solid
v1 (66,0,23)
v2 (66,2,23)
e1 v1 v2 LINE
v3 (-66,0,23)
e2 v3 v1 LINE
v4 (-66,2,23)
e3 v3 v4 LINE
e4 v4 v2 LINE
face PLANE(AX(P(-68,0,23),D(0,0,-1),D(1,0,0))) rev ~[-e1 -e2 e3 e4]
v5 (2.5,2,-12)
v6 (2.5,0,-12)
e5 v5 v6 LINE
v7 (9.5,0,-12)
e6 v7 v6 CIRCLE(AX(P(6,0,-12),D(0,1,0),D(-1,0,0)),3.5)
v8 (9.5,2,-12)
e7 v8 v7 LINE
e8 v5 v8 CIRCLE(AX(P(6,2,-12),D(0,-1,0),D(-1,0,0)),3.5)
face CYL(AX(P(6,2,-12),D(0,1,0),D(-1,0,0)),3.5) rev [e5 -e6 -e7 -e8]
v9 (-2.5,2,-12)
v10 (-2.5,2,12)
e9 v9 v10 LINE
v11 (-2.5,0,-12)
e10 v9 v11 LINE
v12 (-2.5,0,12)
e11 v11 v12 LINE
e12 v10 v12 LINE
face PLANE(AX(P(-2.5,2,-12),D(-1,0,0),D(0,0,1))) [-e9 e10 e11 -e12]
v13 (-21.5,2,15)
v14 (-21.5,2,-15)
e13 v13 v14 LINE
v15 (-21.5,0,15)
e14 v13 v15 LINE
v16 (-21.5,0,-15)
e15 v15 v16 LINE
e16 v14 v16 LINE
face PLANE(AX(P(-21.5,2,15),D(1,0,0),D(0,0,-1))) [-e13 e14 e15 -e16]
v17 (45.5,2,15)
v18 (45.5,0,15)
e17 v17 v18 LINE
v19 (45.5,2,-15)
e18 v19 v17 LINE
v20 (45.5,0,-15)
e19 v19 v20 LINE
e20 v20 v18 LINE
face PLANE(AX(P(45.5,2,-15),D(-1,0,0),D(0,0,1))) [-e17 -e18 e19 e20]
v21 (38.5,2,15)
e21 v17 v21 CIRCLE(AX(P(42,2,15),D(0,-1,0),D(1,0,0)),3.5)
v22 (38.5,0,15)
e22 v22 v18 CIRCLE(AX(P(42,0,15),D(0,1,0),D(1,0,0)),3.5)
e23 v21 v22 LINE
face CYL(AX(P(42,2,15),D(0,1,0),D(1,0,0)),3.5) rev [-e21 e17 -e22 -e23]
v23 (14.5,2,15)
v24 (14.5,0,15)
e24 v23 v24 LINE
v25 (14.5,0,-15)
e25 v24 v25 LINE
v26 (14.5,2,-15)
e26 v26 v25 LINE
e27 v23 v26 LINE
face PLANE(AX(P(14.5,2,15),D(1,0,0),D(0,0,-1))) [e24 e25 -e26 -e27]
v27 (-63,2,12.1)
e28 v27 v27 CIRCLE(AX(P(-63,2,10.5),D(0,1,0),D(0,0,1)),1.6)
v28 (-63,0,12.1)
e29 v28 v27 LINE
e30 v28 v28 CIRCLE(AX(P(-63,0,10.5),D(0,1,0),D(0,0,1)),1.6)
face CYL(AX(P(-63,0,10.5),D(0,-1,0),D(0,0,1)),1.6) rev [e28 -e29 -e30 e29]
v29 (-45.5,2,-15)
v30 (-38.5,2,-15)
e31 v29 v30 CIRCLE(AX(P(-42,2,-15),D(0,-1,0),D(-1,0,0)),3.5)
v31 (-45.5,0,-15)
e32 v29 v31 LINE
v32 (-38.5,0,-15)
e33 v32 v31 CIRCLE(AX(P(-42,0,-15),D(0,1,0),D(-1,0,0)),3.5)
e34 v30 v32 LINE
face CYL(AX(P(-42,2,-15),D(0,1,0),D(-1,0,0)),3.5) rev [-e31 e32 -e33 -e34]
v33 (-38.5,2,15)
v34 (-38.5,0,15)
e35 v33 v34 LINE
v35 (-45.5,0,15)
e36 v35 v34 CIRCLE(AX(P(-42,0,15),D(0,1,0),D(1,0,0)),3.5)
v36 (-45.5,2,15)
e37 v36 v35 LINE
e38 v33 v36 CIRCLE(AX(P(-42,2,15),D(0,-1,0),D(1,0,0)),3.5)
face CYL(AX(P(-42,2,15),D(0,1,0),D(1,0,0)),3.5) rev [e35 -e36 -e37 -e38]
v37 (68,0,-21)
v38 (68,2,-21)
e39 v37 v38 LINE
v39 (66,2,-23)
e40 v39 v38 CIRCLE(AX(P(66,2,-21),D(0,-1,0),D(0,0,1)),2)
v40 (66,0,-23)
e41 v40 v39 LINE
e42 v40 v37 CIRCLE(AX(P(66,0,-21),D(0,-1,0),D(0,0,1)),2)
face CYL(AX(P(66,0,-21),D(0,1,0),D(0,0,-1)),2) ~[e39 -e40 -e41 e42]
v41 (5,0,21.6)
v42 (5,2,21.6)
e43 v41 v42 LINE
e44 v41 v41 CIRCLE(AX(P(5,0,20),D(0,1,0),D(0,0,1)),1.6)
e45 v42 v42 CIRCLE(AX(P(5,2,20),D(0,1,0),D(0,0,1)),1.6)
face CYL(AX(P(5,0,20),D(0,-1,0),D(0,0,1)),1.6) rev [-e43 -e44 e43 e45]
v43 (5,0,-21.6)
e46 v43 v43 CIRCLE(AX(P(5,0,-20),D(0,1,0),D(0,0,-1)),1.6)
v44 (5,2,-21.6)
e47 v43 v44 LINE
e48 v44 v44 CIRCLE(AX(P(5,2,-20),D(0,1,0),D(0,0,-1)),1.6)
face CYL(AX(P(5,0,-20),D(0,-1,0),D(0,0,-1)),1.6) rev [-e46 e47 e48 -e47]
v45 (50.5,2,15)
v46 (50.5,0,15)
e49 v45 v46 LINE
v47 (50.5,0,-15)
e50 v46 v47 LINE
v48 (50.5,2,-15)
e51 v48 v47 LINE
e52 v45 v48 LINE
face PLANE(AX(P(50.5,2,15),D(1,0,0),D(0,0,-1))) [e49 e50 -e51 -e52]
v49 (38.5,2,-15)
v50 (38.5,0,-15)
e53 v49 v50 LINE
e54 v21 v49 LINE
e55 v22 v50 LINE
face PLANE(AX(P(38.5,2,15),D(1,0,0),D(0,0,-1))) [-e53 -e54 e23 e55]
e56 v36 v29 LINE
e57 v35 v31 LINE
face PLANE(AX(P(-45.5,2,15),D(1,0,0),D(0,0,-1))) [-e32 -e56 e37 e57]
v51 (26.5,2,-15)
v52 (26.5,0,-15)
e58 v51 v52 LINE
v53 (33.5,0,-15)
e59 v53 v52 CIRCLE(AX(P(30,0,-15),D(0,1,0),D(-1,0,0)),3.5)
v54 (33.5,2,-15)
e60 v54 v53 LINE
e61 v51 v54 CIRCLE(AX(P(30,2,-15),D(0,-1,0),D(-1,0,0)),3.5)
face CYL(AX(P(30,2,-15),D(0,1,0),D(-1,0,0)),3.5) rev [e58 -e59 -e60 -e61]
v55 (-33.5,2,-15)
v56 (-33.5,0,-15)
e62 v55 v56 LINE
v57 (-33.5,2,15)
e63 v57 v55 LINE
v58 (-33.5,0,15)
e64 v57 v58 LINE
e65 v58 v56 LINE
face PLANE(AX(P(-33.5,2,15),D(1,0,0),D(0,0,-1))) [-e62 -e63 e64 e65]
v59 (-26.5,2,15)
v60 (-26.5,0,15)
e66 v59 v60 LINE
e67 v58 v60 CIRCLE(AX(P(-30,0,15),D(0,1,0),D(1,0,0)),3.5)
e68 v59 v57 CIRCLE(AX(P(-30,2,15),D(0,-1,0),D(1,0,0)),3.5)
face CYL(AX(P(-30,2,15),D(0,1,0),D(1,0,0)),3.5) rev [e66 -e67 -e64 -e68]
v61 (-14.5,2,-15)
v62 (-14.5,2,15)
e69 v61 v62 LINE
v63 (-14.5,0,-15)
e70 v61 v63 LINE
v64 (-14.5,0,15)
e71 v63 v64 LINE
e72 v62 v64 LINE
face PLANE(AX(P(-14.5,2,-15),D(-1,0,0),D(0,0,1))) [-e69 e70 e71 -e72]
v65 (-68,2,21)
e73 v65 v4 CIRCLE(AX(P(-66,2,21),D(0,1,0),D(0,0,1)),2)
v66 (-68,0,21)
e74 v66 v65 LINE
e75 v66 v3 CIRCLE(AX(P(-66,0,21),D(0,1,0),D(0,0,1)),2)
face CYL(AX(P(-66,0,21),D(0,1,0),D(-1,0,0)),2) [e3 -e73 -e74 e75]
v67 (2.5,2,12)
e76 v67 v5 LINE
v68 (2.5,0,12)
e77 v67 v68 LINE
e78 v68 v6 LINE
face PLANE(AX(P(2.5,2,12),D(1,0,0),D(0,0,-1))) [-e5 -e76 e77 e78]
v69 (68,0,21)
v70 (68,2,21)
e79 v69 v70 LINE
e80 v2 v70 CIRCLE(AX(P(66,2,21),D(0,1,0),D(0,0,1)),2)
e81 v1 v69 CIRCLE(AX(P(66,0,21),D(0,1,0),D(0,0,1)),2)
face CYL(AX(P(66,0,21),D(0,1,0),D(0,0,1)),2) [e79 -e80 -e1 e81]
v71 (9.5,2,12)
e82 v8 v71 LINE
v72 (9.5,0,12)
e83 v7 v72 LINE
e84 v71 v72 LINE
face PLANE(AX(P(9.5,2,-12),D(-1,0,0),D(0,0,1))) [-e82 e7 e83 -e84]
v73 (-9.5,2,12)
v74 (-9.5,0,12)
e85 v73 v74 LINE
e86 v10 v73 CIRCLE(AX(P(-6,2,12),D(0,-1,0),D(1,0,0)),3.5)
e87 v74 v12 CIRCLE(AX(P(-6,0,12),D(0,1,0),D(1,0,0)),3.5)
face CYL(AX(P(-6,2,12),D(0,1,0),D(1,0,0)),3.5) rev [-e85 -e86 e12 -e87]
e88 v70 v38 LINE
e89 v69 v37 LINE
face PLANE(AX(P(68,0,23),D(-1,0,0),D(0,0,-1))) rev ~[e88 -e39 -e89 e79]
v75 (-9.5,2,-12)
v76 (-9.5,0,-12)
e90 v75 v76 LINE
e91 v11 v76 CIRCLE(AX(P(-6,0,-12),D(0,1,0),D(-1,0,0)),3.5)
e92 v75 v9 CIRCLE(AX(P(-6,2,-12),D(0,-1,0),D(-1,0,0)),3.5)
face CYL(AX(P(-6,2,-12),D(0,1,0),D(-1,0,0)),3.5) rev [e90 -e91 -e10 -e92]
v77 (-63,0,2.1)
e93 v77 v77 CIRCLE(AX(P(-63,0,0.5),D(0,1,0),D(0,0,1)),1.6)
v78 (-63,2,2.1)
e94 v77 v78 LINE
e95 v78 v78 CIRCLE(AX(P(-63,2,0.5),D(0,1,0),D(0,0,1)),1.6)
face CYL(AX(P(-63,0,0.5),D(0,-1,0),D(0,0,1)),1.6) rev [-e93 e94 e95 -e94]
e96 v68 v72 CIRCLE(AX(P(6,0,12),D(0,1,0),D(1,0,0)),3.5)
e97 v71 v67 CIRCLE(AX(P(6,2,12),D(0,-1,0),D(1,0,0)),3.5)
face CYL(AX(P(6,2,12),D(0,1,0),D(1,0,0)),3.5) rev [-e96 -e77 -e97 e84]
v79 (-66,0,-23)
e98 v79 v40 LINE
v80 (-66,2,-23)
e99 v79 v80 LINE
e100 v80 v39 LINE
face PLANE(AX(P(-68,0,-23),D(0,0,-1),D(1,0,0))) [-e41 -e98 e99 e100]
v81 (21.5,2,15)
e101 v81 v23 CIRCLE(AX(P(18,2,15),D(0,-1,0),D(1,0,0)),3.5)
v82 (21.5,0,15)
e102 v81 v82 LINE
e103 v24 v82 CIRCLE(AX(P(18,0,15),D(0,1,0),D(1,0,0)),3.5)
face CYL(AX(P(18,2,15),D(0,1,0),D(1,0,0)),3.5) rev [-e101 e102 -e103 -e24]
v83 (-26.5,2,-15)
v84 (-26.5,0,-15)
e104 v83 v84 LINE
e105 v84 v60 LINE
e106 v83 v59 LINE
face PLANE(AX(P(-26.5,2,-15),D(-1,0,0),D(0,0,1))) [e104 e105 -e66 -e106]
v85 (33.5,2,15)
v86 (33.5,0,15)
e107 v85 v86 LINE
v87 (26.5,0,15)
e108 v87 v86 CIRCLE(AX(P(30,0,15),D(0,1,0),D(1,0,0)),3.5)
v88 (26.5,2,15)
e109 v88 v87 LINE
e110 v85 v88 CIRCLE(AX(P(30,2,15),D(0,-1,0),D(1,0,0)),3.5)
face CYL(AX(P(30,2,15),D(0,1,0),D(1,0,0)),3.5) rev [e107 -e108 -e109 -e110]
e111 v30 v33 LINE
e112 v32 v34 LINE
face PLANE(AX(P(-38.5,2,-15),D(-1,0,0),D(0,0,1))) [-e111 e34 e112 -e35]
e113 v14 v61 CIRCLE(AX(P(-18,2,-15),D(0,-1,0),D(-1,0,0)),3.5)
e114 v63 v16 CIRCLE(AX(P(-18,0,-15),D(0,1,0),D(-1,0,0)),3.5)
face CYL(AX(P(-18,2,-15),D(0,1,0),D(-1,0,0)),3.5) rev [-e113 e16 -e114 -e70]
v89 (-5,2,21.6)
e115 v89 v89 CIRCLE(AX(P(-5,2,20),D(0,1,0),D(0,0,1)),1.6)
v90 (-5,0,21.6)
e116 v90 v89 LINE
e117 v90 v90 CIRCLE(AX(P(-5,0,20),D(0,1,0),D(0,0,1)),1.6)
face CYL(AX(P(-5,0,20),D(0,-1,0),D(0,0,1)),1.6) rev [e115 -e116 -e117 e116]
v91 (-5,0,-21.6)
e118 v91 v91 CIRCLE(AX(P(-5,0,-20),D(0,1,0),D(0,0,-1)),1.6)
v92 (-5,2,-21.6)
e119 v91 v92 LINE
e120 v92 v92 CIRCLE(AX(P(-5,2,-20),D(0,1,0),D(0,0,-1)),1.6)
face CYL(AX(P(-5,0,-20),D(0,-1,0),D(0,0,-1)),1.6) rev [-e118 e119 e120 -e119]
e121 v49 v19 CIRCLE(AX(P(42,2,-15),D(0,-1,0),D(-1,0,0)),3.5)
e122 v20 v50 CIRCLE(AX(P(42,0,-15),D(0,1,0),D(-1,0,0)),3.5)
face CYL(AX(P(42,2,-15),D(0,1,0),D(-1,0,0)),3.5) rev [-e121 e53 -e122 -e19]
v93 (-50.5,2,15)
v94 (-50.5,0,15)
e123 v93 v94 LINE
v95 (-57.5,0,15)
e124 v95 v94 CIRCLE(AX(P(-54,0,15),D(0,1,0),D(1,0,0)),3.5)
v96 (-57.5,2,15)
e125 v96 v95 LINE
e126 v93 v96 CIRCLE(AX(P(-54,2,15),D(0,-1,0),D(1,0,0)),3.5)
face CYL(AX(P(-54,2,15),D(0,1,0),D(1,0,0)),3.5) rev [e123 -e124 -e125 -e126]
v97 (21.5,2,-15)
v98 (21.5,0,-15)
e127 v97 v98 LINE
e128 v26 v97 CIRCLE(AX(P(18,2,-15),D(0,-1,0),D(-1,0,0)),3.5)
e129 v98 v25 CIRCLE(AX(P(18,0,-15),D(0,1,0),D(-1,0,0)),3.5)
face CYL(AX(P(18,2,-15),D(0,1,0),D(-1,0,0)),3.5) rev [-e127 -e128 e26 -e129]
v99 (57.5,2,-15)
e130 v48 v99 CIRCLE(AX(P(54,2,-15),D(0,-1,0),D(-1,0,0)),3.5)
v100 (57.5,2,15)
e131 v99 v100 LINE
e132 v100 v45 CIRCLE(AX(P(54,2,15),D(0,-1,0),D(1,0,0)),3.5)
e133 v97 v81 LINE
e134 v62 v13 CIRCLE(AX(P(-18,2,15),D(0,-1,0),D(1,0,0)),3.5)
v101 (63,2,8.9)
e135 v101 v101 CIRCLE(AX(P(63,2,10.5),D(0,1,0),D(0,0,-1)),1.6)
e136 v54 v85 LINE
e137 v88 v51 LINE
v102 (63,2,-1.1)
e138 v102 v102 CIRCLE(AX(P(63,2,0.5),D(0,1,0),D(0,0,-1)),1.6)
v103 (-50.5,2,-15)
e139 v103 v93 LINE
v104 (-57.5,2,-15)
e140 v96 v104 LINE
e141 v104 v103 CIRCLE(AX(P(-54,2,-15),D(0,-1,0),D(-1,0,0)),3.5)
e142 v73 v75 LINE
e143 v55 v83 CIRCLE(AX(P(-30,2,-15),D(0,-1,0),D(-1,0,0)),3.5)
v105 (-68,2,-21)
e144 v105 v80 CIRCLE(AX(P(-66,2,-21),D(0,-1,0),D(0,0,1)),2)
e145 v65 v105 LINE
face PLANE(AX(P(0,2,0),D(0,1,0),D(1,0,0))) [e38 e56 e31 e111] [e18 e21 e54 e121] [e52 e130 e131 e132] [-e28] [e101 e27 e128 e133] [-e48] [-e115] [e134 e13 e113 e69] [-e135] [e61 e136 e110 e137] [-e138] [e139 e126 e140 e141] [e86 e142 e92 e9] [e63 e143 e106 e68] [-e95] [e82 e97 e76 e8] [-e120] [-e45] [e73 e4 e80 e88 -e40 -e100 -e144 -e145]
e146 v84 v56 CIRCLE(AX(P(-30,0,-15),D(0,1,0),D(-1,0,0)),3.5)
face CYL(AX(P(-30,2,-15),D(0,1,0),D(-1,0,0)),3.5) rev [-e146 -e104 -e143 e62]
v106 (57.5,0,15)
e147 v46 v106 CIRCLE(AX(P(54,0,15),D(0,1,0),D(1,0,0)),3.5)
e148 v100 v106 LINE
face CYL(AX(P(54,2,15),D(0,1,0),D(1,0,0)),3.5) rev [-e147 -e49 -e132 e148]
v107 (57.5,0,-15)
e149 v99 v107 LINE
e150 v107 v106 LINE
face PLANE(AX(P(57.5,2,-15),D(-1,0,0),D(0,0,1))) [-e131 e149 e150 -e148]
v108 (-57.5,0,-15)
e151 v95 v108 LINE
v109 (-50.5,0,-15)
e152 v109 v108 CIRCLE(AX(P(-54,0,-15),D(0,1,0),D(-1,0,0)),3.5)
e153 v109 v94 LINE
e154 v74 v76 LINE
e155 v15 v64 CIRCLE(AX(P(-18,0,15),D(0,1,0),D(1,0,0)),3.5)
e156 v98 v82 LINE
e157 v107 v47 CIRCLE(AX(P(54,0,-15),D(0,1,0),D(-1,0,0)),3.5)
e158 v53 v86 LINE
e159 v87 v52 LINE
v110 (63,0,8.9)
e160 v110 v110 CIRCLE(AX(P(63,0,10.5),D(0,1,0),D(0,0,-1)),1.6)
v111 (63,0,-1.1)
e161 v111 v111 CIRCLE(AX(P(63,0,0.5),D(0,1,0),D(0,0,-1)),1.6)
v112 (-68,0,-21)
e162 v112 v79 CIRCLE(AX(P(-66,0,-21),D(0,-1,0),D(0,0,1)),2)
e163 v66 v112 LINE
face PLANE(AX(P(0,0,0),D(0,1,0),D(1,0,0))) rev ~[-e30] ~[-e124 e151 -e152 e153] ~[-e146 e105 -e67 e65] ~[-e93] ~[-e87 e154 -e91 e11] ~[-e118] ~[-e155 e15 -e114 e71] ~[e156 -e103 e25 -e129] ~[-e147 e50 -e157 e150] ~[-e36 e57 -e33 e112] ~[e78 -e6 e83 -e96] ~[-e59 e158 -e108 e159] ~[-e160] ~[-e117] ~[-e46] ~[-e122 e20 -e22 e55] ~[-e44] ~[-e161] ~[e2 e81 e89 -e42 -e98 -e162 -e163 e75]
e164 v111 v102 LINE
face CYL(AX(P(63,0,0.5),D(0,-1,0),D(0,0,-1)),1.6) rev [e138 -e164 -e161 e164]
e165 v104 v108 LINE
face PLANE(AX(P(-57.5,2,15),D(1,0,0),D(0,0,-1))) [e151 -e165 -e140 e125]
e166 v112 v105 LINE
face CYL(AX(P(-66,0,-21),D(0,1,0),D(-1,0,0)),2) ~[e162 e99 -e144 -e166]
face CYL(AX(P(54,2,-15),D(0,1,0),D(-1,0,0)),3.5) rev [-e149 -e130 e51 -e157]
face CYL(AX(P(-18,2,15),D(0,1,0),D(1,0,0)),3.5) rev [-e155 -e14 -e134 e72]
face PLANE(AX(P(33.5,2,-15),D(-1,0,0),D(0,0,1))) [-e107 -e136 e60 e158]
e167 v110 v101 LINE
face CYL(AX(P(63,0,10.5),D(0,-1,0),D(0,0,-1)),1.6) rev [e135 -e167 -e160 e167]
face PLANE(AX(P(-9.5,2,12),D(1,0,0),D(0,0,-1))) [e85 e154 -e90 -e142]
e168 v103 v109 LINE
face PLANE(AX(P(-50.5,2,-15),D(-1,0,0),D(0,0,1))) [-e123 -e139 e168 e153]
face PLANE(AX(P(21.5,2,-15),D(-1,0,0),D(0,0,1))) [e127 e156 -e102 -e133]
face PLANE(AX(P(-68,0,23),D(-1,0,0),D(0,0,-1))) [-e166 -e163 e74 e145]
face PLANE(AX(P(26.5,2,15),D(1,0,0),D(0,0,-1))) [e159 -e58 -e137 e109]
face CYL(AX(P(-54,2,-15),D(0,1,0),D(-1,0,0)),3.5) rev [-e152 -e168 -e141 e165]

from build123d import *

# Parameters (mm, degrees)
SKETCH1_W           = 136
SKETCH1_H           = 46
SKETCH1_R           = 1.6
BOSS_EXTRUDE1_DEPTH = 2
CUT_EXTRUDE1_DEPTH  = 72.812255222
R2_FILLET_1_R       = 2


with BuildPart() as part:
    # Sketch1 → Boss-Extrude1 (new body)
    with BuildSketch(Plane(origin=(0, 0, 0), x_dir=(1, 0, 0), z_dir=(0, 1, 0))):
        Rectangle(SKETCH1_W, SKETCH1_H)
        with Locations(Location((-63, -0.5, 0), (0, 0, 270))):
            Circle(SKETCH1_R, mode=Mode.SUBTRACT)
        with Locations(Location((-63, -10.5, 0), (0, 0, 270))):
            Circle(SKETCH1_R, mode=Mode.SUBTRACT)
        with Locations(Location((-5, -20, 0), (0, 0, 270))):
            Circle(SKETCH1_R, mode=Mode.SUBTRACT)
        with Locations(Location((5, -20, 0), (0, 0, 270))):
            Circle(SKETCH1_R, mode=Mode.SUBTRACT)
        with Locations(Location((63, -10.5, 0), (0, 0, 90))):
            Circle(SKETCH1_R, mode=Mode.SUBTRACT)
        with Locations(Location((63, -0.5, 0), (0, 0, 90))):
            Circle(SKETCH1_R, mode=Mode.SUBTRACT)
        with Locations(Location((5, 20, 0), (0, 0, 90))):
            Circle(SKETCH1_R, mode=Mode.SUBTRACT)
        with Locations(Location((-5, 20, 0), (0, 0, 90))):
            Circle(SKETCH1_R, mode=Mode.SUBTRACT)
    extrude(amount=BOSS_EXTRUDE1_DEPTH)

    # Sketch2 → Cut-Extrude1 (cut, through all)
    with BuildSketch(Plane(origin=(0, 2, 0), x_dir=(1, 0, 0), z_dir=(0, 1, 0))):
        with BuildLine():
            Line((-50.5, 15), (-50.5, -15))
            ThreePointArc((-50.5, -15), (-54, -18.5), (-57.5, -15))
            Line((-57.5, -15), (-57.5, 15))
            ThreePointArc((-57.5, 15), (-54, 18.5), (-50.5, 15))
        make_face()
        with BuildLine():
            Line((-38.5, 15), (-38.5, -15))
            ThreePointArc((-38.5, -15), (-42, -18.5), (-45.5, -15))
            Line((-45.5, -15), (-45.5, 15))
            ThreePointArc((-45.5, 15), (-42, 18.5), (-38.5, 15))
        make_face()
        with BuildLine():
            Line((-26.5, 15), (-26.5, -15))
            ThreePointArc((-26.5, -15), (-30, -18.5), (-33.5, -15))
            Line((-33.5, -15), (-33.5, 15))
            ThreePointArc((-33.5, 15), (-30, 18.5), (-26.5, 15))
        make_face()
        with BuildLine():
            Line((-14.5, 15), (-14.5, -15))
            ThreePointArc((-14.5, -15), (-18, -18.5), (-21.5, -15))
            Line((-21.5, -15), (-21.5, 15))
            ThreePointArc((-21.5, 15), (-18, 18.5), (-14.5, 15))
        make_face()
        with BuildLine():
            Line((-2.5, 12), (-2.5, -12))
            ThreePointArc((-2.5, -12), (-6, -15.5), (-9.5, -12))
            Line((-9.5, -12), (-9.5, 12))
            ThreePointArc((-9.5, 12), (-6, 15.5), (-2.5, 12))
        make_face()
        with BuildLine():
            Line((9.5, 12), (9.5, -12))
            ThreePointArc((9.5, -12), (6, -15.5), (2.5, -12))
            Line((2.5, -12), (2.5, 12))
            ThreePointArc((2.5, 12), (6, 15.5), (9.5, 12))
        make_face()
        with BuildLine():
            Line((21.5, 15), (21.5, -15))
            ThreePointArc((21.5, -15), (18, -18.5), (14.5, -15))
            Line((14.5, -15), (14.5, 15))
            ThreePointArc((14.5, 15), (18, 18.5), (21.5, 15))
        make_face()
        with BuildLine():
            Line((33.5, 15), (33.5, -15))
            ThreePointArc((33.5, -15), (30, -18.5), (26.5, -15))
            Line((26.5, -15), (26.5, 15))
            ThreePointArc((26.5, 15), (30, 18.5), (33.5, 15))
        make_face()
        with BuildLine():
            Line((45.5, 15), (45.5, -15))
            ThreePointArc((45.5, -15), (42, -18.5), (38.5, -15))
            Line((38.5, -15), (38.5, 15))
            ThreePointArc((38.5, 15), (42, 18.5), (45.5, 15))
        make_face()
        with BuildLine():
            Line((57.5, 15), (57.5, -15))
            ThreePointArc((57.5, -15), (54, -18.5), (50.5, -15))
            Line((50.5, -15), (50.5, 15))
            ThreePointArc((50.5, 15), (54, 18.5), (57.5, 15))
        make_face()
    extrude(amount=-CUT_EXTRUDE1_DEPTH, mode=Mode.SUBTRACT)

    # R2 Fillet 1
    r2_fillet_1_edges = [part.edges().sort_by_distance(p)[0] for p in [
        (-68, 1, -23),
        (68, 1, -23),
        (68, 1, 23),
        (-68, 1, 23),
    ]]
    fillet(r2_fillet_1_edges, radius=R2_FILLET_1_R)


solid = part.part
